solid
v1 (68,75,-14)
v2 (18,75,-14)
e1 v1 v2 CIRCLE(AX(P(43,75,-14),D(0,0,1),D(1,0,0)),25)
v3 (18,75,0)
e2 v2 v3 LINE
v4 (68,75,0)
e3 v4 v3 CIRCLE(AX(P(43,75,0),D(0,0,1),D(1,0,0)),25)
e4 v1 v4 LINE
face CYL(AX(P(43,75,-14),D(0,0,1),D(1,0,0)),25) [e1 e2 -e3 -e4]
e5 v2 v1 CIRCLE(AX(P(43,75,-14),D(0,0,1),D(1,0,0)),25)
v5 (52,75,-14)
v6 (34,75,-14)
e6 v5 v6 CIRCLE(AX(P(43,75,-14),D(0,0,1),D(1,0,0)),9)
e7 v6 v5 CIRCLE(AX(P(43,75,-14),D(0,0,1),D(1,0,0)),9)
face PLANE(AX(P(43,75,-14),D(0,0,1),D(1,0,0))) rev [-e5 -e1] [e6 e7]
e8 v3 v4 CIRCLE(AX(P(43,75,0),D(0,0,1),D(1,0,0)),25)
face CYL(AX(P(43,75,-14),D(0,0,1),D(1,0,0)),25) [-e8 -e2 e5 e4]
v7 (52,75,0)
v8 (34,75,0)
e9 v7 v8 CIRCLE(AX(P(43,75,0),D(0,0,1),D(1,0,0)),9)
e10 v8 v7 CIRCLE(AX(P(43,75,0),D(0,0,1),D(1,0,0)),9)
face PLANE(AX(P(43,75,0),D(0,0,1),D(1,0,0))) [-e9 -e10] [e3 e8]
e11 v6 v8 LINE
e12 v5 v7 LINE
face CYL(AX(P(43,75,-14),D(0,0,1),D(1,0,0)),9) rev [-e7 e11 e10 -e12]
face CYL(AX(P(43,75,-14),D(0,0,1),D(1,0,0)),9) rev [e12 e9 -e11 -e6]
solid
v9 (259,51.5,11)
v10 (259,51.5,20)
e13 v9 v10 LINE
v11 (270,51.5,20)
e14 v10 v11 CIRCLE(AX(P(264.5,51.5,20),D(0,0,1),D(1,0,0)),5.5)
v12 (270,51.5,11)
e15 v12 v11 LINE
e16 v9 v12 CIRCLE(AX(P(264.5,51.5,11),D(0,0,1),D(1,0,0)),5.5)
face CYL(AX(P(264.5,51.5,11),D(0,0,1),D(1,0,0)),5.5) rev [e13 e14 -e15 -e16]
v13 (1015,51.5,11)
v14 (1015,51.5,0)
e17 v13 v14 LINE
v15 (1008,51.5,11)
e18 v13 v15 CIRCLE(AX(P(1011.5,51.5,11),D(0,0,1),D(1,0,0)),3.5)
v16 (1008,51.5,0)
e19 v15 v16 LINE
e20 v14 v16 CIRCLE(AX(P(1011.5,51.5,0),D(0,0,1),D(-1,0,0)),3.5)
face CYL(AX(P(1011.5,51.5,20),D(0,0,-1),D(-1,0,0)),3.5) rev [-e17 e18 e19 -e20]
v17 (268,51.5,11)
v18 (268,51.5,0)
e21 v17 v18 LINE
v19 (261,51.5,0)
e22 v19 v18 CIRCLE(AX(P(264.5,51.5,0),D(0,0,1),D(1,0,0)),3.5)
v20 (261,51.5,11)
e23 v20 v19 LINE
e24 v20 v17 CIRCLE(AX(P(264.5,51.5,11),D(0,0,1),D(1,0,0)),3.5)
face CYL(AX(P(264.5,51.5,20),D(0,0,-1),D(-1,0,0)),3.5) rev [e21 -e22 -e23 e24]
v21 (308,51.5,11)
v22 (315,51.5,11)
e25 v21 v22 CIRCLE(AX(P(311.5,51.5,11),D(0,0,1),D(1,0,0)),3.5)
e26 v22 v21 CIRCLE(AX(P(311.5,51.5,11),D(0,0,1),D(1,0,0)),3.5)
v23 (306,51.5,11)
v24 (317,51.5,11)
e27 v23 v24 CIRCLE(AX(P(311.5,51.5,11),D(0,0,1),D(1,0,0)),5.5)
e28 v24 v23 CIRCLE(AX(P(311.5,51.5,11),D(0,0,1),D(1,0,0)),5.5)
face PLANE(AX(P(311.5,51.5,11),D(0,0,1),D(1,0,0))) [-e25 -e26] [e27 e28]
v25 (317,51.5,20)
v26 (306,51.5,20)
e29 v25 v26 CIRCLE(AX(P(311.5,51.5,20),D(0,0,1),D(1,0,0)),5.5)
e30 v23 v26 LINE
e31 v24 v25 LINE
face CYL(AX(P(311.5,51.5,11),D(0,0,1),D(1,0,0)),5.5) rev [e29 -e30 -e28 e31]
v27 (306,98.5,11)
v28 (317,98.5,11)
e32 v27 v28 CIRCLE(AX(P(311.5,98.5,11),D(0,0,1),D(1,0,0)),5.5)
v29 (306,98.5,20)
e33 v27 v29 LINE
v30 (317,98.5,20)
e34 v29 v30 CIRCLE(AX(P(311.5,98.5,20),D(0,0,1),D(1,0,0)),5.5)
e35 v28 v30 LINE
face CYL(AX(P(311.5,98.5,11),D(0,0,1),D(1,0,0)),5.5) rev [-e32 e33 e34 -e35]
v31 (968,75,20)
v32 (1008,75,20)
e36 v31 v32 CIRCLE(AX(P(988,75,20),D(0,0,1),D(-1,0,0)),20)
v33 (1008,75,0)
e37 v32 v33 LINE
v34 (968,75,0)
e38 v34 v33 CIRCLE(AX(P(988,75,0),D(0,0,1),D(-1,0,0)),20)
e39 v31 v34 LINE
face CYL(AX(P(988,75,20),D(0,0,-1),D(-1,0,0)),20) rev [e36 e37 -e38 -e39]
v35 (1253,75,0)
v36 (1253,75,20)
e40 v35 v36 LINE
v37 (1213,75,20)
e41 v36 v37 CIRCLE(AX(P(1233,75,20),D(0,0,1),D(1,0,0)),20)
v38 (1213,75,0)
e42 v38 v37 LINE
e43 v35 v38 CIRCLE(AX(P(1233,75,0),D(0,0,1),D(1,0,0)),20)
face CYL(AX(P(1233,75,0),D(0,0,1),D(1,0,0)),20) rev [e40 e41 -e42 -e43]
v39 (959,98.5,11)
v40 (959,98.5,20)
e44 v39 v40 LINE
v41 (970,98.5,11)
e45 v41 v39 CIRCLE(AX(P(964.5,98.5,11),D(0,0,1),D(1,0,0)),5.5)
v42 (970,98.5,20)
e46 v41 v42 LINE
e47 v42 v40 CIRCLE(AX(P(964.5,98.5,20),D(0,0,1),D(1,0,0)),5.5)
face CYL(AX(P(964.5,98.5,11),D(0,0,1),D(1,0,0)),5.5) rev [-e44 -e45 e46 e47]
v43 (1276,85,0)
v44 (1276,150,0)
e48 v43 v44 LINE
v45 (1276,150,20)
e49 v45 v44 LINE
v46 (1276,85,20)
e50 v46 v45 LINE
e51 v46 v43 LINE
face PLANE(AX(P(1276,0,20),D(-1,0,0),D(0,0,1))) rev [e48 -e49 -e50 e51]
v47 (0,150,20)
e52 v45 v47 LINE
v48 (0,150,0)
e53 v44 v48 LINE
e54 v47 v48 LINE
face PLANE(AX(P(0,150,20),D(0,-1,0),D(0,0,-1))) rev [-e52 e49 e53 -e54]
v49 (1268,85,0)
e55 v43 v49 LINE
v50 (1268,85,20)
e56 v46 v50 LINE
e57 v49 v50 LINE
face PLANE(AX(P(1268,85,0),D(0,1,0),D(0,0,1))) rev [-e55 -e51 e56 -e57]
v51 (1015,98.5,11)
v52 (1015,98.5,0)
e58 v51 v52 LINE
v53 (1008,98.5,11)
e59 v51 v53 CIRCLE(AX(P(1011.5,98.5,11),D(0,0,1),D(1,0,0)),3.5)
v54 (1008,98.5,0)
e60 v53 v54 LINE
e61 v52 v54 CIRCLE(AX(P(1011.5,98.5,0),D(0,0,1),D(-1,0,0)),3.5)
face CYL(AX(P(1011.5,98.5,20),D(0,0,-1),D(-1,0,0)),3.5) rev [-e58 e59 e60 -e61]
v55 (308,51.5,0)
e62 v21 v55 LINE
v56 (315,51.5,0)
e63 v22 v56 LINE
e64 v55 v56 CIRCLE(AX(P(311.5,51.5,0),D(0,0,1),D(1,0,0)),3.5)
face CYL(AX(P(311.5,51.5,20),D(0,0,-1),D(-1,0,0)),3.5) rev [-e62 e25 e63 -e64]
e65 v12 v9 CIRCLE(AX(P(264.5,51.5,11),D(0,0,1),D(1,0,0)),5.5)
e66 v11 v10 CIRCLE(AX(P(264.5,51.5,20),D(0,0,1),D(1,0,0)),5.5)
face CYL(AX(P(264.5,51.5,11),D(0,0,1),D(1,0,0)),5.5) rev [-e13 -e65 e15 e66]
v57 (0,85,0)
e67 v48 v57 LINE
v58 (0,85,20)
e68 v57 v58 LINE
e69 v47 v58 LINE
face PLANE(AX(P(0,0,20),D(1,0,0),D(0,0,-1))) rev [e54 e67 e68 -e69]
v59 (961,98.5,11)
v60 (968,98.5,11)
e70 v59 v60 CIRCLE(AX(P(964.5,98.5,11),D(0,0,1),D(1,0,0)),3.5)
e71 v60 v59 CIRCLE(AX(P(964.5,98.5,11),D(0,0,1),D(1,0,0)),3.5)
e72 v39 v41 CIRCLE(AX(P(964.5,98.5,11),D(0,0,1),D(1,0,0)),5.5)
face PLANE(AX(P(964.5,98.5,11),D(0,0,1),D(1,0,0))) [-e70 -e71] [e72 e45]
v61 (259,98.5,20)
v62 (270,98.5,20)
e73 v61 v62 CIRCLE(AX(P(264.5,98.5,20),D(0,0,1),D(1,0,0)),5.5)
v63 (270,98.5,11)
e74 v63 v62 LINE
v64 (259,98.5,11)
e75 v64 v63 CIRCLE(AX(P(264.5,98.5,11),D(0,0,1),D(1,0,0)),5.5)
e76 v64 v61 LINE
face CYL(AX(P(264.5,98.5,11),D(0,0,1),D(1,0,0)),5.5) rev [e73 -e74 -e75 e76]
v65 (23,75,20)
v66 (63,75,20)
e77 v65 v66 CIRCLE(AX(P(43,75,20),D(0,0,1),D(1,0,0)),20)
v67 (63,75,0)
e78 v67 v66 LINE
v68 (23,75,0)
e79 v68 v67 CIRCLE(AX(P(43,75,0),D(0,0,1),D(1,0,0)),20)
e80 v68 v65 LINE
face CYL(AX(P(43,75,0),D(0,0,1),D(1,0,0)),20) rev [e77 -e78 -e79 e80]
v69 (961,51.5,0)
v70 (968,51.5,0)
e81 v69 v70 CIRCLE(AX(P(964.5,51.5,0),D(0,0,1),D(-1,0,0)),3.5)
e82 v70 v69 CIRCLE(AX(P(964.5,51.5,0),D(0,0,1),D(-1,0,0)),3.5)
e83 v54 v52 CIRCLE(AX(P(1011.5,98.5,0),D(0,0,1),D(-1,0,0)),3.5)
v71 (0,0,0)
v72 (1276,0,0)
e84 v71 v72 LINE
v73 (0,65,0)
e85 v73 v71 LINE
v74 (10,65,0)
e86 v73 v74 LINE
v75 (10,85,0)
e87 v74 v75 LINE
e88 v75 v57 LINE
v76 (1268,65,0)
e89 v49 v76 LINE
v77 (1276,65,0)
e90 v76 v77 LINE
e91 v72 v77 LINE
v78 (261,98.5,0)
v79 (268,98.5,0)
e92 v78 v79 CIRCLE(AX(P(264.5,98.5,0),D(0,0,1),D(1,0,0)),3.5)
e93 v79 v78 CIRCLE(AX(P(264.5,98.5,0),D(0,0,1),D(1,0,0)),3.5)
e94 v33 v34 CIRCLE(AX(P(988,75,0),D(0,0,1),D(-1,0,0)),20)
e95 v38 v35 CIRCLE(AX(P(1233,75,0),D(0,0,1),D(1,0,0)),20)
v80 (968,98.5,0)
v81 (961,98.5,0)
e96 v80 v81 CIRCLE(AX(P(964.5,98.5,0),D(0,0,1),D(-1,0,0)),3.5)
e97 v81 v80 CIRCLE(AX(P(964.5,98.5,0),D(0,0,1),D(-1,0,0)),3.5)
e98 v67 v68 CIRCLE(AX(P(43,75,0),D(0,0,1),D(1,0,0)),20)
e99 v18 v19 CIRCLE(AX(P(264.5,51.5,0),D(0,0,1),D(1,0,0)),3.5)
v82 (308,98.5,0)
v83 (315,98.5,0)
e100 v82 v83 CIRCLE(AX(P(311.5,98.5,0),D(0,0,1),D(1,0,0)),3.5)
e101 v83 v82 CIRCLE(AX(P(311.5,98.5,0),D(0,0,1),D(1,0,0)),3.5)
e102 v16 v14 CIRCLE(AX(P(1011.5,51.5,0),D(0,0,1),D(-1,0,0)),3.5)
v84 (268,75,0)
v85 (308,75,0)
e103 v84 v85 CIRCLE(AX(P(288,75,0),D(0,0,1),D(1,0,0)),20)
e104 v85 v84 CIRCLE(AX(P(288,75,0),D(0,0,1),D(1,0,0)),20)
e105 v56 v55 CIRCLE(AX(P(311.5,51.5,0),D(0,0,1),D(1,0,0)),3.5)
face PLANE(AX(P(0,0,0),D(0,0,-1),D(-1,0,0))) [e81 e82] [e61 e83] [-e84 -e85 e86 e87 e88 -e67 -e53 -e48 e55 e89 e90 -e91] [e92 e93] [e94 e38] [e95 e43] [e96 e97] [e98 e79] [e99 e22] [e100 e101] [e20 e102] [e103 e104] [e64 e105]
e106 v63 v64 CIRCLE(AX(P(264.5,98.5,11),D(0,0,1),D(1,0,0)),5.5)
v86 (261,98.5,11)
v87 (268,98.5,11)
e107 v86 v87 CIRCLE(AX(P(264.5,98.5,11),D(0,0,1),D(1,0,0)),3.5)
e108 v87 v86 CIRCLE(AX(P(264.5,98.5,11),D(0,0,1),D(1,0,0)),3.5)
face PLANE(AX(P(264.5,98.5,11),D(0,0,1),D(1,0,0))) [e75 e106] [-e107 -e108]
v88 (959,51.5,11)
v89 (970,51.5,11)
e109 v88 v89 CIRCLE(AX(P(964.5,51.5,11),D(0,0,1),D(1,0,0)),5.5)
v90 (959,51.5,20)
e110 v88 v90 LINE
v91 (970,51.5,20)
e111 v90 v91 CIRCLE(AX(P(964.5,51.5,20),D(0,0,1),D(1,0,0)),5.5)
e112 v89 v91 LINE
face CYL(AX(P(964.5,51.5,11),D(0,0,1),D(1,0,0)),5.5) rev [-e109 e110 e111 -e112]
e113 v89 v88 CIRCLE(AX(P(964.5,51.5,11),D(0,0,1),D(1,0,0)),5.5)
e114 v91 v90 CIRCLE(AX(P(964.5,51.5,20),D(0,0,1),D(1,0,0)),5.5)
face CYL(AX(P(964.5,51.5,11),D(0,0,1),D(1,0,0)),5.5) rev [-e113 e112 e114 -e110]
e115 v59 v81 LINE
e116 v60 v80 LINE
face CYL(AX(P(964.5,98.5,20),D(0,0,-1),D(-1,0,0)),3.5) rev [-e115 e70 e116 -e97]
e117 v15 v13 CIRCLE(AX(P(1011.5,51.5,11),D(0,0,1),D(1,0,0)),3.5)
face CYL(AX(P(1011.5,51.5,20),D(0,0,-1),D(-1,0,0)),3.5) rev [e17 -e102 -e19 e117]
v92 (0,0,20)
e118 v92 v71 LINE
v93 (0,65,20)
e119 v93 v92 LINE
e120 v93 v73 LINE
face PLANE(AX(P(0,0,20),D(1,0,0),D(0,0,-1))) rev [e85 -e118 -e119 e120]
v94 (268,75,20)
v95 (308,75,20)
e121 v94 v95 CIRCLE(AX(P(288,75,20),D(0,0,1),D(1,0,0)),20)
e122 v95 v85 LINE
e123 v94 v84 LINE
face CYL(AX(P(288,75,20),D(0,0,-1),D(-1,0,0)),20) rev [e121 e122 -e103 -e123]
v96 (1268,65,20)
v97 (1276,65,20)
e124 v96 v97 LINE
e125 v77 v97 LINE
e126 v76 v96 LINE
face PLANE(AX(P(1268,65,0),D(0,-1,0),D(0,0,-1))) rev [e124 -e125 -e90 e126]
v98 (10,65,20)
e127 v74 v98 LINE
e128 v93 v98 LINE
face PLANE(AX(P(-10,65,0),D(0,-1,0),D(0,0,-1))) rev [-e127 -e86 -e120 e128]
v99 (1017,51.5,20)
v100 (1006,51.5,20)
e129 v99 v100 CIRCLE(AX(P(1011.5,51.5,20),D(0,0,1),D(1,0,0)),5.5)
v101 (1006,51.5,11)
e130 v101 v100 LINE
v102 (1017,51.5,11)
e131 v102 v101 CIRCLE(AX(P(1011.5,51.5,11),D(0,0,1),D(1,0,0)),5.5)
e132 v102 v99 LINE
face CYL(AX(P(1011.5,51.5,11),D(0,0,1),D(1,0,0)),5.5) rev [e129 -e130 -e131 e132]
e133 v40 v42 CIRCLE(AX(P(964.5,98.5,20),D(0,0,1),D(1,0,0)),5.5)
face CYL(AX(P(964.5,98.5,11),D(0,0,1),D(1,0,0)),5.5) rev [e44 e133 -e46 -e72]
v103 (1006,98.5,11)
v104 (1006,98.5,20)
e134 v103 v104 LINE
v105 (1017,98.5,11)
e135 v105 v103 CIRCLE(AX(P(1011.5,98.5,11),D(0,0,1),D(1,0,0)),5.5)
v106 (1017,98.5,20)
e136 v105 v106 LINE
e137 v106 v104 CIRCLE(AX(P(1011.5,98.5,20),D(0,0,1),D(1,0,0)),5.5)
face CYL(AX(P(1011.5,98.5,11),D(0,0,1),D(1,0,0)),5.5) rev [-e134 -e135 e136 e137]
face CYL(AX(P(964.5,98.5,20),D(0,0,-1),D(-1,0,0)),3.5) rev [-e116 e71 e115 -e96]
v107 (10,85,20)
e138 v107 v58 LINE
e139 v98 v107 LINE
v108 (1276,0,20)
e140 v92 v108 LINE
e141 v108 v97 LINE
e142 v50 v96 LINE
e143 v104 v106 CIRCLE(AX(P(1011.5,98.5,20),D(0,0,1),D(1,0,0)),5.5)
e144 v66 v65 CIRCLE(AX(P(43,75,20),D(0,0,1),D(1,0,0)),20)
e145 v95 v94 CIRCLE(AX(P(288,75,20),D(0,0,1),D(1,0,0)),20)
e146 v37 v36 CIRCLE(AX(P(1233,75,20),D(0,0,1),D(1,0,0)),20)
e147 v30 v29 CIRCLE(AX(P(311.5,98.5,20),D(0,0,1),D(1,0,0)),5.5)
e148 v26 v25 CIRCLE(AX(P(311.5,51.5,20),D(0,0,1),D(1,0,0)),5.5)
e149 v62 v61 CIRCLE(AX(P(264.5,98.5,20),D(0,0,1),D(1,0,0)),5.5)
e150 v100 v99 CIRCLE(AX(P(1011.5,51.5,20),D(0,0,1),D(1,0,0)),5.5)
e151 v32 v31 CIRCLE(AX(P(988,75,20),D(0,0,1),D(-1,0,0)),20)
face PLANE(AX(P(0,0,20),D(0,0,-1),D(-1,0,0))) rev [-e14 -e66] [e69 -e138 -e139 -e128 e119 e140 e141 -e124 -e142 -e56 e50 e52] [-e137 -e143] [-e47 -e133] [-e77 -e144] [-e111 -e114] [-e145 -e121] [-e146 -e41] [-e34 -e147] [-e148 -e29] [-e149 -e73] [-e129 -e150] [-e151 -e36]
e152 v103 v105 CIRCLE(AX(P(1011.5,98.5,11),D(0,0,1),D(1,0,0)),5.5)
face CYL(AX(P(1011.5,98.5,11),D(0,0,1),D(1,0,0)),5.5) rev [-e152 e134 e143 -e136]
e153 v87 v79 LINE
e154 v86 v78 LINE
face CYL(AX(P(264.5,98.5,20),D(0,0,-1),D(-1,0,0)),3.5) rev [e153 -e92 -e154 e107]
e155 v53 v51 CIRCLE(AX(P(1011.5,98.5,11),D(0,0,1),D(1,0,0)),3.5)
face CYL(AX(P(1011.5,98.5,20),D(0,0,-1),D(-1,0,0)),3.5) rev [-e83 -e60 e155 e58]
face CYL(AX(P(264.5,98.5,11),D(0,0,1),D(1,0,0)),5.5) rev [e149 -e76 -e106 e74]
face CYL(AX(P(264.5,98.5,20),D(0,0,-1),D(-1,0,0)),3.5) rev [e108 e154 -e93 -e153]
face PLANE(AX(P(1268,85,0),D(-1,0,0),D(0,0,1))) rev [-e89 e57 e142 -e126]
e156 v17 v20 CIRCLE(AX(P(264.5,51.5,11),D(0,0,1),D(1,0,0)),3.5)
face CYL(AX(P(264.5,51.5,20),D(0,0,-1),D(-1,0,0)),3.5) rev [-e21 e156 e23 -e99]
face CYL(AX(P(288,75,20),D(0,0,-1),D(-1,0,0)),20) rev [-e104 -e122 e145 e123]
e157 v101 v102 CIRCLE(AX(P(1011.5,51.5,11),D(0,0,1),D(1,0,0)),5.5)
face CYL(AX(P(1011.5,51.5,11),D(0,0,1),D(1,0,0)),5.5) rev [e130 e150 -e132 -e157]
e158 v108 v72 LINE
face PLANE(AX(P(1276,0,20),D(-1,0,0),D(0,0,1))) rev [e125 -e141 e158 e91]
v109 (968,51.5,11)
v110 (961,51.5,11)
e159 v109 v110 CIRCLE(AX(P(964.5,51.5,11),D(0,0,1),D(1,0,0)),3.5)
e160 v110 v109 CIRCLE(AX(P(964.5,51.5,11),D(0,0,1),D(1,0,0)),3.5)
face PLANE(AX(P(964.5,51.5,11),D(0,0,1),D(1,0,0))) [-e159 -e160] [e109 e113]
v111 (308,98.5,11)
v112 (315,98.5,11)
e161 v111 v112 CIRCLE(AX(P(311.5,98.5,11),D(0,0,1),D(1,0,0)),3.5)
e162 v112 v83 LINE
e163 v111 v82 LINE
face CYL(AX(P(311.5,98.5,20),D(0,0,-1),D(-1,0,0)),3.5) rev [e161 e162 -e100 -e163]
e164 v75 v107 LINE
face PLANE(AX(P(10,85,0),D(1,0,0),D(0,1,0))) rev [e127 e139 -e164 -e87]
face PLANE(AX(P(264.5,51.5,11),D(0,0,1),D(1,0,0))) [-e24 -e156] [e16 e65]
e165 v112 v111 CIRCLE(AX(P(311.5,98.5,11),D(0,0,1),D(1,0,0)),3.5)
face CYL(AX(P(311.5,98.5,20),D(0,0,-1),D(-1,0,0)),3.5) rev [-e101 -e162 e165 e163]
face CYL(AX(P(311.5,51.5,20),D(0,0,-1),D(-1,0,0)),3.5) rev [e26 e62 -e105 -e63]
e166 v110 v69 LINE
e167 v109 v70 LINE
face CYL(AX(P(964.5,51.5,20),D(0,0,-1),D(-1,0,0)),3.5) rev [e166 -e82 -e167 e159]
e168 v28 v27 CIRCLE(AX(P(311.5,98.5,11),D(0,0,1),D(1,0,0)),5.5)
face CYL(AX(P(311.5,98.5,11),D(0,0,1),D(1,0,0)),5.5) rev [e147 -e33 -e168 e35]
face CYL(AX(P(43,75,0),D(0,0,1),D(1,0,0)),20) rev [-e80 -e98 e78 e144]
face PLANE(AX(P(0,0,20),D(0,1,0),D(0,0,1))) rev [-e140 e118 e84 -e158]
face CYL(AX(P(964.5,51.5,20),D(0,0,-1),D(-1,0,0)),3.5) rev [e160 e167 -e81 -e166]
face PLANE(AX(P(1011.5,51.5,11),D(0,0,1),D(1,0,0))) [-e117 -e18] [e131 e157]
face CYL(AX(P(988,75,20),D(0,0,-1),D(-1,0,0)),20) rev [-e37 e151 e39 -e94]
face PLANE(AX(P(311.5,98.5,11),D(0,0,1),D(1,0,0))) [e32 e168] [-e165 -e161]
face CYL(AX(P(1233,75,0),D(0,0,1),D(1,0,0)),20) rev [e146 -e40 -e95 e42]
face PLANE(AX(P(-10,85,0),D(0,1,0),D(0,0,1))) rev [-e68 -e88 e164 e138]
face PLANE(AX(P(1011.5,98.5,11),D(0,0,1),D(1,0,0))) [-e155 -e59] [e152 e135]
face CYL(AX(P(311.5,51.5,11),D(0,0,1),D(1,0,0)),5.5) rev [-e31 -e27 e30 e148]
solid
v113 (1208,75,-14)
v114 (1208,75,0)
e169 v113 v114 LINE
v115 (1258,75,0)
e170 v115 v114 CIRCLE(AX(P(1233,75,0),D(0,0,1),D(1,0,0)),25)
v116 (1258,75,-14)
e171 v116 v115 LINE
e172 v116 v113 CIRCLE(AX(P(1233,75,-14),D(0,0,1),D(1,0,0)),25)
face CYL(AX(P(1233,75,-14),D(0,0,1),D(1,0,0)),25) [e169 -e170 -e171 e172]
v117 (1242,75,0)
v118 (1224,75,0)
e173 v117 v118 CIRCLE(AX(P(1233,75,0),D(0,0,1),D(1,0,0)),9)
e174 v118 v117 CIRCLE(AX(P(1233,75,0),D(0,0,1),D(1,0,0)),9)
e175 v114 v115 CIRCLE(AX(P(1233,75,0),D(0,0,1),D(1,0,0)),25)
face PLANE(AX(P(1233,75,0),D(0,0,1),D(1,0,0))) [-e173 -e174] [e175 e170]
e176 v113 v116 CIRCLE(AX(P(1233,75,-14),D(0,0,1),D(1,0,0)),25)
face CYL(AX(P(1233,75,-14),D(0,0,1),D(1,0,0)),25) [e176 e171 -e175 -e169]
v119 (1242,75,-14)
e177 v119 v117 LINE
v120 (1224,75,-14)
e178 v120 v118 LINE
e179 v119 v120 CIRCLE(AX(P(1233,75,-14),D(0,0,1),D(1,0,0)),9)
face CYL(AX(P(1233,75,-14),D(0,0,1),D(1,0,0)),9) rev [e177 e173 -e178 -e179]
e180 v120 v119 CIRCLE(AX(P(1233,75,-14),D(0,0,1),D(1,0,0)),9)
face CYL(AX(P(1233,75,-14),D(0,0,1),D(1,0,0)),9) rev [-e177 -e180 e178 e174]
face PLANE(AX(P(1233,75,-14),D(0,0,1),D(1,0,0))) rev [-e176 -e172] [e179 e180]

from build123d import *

# Parameters (mm, degrees)
SKETCH1_W             = 1276
SKETCH1_H             = 150
SKETCH1_R             = 20
SKETCH1_R_2           = 3.5
BOSS_EXTRUDE1_DEPTH   = 20
SKETCH2_R             = 5.5
CUT_EXTRUDE1_DEPTH    = 9
SKETCH4_W             = 20
SKETCH4_H             = 20
SKETCH4_W_2           = 16
CUT_EXTRUDE2_DEPTH    = 1285.942022038
SKETCH5_R             = 20
CUT_EXTRUDE3_DEPTH    = 1285.942022038
SKETCH6_R             = 25
SKETCH6_R_2           = 9
BOSS_EXTRUDE2_DEPTH   = 14
BOSS_EXTRUDE2_2_DEPTH = 14


with BuildPart() as part:
    # Sketch1 → Boss-Extrude1 (new body)
    with BuildSketch(Plane.XY):
        with Locations((638, 75)):
            Rectangle(SKETCH1_W, SKETCH1_H)
        with Locations((288, 75)):
            Circle(SKETCH1_R, mode=Mode.SUBTRACT)
        with Locations((264.5, 98.5)):
            Circle(SKETCH1_R_2, mode=Mode.SUBTRACT)
        with Locations((311.5, 98.5)):
            Circle(SKETCH1_R_2, mode=Mode.SUBTRACT)
        with Locations((311.5, 51.5)):
            Circle(SKETCH1_R_2, mode=Mode.SUBTRACT)
        with Locations((264.5, 51.5)):
            Circle(SKETCH1_R_2, mode=Mode.SUBTRACT)
        with Locations(Location((964.5, 51.5, 0), (0, 0, 180))):
            Circle(SKETCH1_R_2, mode=Mode.SUBTRACT)
        with Locations(Location((1011.5, 51.5, 0), (0, 0, 180))):
            Circle(SKETCH1_R_2, mode=Mode.SUBTRACT)
        with Locations(Location((988, 75, 0), (0, 0, 180))):
            Circle(SKETCH1_R, mode=Mode.SUBTRACT)
        with Locations(Location((1011.5, 98.5, 0), (0, 0, 180))):
            Circle(SKETCH1_R_2, mode=Mode.SUBTRACT)
        with Locations(Location((964.5, 98.5, 0), (0, 0, 180))):
            Circle(SKETCH1_R_2, mode=Mode.SUBTRACT)
    extrude(amount=BOSS_EXTRUDE1_DEPTH)

    # Sketch2 → Cut-Extrude1 (cut)
    with BuildSketch(Plane.XY.offset(20)):
        with Locations((264.5, 98.5)):
            Circle(SKETCH2_R)
        with Locations((311.5, 98.5)):
            Circle(SKETCH2_R)
        with Locations((311.5, 51.5)):
            Circle(SKETCH2_R)
        with Locations((264.5, 51.5)):
            Circle(SKETCH2_R)
        with Locations((964.5, 98.5)):
            Circle(SKETCH2_R)
        with Locations((1011.5, 98.5)):
            Circle(SKETCH2_R)
        with Locations((1011.5, 51.5)):
            Circle(SKETCH2_R)
        with Locations((964.5, 51.5)):
            Circle(SKETCH2_R)
    extrude(amount=-CUT_EXTRUDE1_DEPTH, mode=Mode.SUBTRACT)

    # Sketch4 → Cut-Extrude2 (cut, through all)
    with BuildSketch(Plane.XY.offset(20)):
        with Locations((0, 75)):
            Rectangle(SKETCH4_W, SKETCH4_H)
        with Locations((1276, 75)):
            Rectangle(SKETCH4_W_2, SKETCH4_H)
    extrude(amount=-CUT_EXTRUDE2_DEPTH, mode=Mode.SUBTRACT)

    # Sketch5 → Cut-Extrude3 (cut, through all)
    with BuildSketch(Plane.XY.offset(20)):
        with Locations((43, 75)):
            Circle(SKETCH5_R)
        with Locations((1233, 75)):
            Circle(SKETCH5_R)
    extrude(amount=-CUT_EXTRUDE3_DEPTH, mode=Mode.SUBTRACT)


with BuildPart() as body_2:
    # Sketch6 → Boss-Extrude2 (new body)
    with BuildSketch(Plane.XY):
        with Locations((43, 75)):
            Circle(SKETCH6_R)
        with Locations((43, 75)):
            Circle(SKETCH6_R_2, mode=Mode.SUBTRACT)
    extrude(amount=-BOSS_EXTRUDE2_DEPTH)


with BuildPart() as body_3:
    # Sketch6 → Boss-Extrude2 2 (new body)
    with BuildSketch(Plane.XY):
        with Locations((1233, 75)):
            Circle(SKETCH6_R)
        with Locations((1233, 75)):
            Circle(SKETCH6_R_2, mode=Mode.SUBTRACT)
    extrude(amount=-BOSS_EXTRUDE2_2_DEPTH)


solid = Compound([part.part, body_2.part, body_3.part])
